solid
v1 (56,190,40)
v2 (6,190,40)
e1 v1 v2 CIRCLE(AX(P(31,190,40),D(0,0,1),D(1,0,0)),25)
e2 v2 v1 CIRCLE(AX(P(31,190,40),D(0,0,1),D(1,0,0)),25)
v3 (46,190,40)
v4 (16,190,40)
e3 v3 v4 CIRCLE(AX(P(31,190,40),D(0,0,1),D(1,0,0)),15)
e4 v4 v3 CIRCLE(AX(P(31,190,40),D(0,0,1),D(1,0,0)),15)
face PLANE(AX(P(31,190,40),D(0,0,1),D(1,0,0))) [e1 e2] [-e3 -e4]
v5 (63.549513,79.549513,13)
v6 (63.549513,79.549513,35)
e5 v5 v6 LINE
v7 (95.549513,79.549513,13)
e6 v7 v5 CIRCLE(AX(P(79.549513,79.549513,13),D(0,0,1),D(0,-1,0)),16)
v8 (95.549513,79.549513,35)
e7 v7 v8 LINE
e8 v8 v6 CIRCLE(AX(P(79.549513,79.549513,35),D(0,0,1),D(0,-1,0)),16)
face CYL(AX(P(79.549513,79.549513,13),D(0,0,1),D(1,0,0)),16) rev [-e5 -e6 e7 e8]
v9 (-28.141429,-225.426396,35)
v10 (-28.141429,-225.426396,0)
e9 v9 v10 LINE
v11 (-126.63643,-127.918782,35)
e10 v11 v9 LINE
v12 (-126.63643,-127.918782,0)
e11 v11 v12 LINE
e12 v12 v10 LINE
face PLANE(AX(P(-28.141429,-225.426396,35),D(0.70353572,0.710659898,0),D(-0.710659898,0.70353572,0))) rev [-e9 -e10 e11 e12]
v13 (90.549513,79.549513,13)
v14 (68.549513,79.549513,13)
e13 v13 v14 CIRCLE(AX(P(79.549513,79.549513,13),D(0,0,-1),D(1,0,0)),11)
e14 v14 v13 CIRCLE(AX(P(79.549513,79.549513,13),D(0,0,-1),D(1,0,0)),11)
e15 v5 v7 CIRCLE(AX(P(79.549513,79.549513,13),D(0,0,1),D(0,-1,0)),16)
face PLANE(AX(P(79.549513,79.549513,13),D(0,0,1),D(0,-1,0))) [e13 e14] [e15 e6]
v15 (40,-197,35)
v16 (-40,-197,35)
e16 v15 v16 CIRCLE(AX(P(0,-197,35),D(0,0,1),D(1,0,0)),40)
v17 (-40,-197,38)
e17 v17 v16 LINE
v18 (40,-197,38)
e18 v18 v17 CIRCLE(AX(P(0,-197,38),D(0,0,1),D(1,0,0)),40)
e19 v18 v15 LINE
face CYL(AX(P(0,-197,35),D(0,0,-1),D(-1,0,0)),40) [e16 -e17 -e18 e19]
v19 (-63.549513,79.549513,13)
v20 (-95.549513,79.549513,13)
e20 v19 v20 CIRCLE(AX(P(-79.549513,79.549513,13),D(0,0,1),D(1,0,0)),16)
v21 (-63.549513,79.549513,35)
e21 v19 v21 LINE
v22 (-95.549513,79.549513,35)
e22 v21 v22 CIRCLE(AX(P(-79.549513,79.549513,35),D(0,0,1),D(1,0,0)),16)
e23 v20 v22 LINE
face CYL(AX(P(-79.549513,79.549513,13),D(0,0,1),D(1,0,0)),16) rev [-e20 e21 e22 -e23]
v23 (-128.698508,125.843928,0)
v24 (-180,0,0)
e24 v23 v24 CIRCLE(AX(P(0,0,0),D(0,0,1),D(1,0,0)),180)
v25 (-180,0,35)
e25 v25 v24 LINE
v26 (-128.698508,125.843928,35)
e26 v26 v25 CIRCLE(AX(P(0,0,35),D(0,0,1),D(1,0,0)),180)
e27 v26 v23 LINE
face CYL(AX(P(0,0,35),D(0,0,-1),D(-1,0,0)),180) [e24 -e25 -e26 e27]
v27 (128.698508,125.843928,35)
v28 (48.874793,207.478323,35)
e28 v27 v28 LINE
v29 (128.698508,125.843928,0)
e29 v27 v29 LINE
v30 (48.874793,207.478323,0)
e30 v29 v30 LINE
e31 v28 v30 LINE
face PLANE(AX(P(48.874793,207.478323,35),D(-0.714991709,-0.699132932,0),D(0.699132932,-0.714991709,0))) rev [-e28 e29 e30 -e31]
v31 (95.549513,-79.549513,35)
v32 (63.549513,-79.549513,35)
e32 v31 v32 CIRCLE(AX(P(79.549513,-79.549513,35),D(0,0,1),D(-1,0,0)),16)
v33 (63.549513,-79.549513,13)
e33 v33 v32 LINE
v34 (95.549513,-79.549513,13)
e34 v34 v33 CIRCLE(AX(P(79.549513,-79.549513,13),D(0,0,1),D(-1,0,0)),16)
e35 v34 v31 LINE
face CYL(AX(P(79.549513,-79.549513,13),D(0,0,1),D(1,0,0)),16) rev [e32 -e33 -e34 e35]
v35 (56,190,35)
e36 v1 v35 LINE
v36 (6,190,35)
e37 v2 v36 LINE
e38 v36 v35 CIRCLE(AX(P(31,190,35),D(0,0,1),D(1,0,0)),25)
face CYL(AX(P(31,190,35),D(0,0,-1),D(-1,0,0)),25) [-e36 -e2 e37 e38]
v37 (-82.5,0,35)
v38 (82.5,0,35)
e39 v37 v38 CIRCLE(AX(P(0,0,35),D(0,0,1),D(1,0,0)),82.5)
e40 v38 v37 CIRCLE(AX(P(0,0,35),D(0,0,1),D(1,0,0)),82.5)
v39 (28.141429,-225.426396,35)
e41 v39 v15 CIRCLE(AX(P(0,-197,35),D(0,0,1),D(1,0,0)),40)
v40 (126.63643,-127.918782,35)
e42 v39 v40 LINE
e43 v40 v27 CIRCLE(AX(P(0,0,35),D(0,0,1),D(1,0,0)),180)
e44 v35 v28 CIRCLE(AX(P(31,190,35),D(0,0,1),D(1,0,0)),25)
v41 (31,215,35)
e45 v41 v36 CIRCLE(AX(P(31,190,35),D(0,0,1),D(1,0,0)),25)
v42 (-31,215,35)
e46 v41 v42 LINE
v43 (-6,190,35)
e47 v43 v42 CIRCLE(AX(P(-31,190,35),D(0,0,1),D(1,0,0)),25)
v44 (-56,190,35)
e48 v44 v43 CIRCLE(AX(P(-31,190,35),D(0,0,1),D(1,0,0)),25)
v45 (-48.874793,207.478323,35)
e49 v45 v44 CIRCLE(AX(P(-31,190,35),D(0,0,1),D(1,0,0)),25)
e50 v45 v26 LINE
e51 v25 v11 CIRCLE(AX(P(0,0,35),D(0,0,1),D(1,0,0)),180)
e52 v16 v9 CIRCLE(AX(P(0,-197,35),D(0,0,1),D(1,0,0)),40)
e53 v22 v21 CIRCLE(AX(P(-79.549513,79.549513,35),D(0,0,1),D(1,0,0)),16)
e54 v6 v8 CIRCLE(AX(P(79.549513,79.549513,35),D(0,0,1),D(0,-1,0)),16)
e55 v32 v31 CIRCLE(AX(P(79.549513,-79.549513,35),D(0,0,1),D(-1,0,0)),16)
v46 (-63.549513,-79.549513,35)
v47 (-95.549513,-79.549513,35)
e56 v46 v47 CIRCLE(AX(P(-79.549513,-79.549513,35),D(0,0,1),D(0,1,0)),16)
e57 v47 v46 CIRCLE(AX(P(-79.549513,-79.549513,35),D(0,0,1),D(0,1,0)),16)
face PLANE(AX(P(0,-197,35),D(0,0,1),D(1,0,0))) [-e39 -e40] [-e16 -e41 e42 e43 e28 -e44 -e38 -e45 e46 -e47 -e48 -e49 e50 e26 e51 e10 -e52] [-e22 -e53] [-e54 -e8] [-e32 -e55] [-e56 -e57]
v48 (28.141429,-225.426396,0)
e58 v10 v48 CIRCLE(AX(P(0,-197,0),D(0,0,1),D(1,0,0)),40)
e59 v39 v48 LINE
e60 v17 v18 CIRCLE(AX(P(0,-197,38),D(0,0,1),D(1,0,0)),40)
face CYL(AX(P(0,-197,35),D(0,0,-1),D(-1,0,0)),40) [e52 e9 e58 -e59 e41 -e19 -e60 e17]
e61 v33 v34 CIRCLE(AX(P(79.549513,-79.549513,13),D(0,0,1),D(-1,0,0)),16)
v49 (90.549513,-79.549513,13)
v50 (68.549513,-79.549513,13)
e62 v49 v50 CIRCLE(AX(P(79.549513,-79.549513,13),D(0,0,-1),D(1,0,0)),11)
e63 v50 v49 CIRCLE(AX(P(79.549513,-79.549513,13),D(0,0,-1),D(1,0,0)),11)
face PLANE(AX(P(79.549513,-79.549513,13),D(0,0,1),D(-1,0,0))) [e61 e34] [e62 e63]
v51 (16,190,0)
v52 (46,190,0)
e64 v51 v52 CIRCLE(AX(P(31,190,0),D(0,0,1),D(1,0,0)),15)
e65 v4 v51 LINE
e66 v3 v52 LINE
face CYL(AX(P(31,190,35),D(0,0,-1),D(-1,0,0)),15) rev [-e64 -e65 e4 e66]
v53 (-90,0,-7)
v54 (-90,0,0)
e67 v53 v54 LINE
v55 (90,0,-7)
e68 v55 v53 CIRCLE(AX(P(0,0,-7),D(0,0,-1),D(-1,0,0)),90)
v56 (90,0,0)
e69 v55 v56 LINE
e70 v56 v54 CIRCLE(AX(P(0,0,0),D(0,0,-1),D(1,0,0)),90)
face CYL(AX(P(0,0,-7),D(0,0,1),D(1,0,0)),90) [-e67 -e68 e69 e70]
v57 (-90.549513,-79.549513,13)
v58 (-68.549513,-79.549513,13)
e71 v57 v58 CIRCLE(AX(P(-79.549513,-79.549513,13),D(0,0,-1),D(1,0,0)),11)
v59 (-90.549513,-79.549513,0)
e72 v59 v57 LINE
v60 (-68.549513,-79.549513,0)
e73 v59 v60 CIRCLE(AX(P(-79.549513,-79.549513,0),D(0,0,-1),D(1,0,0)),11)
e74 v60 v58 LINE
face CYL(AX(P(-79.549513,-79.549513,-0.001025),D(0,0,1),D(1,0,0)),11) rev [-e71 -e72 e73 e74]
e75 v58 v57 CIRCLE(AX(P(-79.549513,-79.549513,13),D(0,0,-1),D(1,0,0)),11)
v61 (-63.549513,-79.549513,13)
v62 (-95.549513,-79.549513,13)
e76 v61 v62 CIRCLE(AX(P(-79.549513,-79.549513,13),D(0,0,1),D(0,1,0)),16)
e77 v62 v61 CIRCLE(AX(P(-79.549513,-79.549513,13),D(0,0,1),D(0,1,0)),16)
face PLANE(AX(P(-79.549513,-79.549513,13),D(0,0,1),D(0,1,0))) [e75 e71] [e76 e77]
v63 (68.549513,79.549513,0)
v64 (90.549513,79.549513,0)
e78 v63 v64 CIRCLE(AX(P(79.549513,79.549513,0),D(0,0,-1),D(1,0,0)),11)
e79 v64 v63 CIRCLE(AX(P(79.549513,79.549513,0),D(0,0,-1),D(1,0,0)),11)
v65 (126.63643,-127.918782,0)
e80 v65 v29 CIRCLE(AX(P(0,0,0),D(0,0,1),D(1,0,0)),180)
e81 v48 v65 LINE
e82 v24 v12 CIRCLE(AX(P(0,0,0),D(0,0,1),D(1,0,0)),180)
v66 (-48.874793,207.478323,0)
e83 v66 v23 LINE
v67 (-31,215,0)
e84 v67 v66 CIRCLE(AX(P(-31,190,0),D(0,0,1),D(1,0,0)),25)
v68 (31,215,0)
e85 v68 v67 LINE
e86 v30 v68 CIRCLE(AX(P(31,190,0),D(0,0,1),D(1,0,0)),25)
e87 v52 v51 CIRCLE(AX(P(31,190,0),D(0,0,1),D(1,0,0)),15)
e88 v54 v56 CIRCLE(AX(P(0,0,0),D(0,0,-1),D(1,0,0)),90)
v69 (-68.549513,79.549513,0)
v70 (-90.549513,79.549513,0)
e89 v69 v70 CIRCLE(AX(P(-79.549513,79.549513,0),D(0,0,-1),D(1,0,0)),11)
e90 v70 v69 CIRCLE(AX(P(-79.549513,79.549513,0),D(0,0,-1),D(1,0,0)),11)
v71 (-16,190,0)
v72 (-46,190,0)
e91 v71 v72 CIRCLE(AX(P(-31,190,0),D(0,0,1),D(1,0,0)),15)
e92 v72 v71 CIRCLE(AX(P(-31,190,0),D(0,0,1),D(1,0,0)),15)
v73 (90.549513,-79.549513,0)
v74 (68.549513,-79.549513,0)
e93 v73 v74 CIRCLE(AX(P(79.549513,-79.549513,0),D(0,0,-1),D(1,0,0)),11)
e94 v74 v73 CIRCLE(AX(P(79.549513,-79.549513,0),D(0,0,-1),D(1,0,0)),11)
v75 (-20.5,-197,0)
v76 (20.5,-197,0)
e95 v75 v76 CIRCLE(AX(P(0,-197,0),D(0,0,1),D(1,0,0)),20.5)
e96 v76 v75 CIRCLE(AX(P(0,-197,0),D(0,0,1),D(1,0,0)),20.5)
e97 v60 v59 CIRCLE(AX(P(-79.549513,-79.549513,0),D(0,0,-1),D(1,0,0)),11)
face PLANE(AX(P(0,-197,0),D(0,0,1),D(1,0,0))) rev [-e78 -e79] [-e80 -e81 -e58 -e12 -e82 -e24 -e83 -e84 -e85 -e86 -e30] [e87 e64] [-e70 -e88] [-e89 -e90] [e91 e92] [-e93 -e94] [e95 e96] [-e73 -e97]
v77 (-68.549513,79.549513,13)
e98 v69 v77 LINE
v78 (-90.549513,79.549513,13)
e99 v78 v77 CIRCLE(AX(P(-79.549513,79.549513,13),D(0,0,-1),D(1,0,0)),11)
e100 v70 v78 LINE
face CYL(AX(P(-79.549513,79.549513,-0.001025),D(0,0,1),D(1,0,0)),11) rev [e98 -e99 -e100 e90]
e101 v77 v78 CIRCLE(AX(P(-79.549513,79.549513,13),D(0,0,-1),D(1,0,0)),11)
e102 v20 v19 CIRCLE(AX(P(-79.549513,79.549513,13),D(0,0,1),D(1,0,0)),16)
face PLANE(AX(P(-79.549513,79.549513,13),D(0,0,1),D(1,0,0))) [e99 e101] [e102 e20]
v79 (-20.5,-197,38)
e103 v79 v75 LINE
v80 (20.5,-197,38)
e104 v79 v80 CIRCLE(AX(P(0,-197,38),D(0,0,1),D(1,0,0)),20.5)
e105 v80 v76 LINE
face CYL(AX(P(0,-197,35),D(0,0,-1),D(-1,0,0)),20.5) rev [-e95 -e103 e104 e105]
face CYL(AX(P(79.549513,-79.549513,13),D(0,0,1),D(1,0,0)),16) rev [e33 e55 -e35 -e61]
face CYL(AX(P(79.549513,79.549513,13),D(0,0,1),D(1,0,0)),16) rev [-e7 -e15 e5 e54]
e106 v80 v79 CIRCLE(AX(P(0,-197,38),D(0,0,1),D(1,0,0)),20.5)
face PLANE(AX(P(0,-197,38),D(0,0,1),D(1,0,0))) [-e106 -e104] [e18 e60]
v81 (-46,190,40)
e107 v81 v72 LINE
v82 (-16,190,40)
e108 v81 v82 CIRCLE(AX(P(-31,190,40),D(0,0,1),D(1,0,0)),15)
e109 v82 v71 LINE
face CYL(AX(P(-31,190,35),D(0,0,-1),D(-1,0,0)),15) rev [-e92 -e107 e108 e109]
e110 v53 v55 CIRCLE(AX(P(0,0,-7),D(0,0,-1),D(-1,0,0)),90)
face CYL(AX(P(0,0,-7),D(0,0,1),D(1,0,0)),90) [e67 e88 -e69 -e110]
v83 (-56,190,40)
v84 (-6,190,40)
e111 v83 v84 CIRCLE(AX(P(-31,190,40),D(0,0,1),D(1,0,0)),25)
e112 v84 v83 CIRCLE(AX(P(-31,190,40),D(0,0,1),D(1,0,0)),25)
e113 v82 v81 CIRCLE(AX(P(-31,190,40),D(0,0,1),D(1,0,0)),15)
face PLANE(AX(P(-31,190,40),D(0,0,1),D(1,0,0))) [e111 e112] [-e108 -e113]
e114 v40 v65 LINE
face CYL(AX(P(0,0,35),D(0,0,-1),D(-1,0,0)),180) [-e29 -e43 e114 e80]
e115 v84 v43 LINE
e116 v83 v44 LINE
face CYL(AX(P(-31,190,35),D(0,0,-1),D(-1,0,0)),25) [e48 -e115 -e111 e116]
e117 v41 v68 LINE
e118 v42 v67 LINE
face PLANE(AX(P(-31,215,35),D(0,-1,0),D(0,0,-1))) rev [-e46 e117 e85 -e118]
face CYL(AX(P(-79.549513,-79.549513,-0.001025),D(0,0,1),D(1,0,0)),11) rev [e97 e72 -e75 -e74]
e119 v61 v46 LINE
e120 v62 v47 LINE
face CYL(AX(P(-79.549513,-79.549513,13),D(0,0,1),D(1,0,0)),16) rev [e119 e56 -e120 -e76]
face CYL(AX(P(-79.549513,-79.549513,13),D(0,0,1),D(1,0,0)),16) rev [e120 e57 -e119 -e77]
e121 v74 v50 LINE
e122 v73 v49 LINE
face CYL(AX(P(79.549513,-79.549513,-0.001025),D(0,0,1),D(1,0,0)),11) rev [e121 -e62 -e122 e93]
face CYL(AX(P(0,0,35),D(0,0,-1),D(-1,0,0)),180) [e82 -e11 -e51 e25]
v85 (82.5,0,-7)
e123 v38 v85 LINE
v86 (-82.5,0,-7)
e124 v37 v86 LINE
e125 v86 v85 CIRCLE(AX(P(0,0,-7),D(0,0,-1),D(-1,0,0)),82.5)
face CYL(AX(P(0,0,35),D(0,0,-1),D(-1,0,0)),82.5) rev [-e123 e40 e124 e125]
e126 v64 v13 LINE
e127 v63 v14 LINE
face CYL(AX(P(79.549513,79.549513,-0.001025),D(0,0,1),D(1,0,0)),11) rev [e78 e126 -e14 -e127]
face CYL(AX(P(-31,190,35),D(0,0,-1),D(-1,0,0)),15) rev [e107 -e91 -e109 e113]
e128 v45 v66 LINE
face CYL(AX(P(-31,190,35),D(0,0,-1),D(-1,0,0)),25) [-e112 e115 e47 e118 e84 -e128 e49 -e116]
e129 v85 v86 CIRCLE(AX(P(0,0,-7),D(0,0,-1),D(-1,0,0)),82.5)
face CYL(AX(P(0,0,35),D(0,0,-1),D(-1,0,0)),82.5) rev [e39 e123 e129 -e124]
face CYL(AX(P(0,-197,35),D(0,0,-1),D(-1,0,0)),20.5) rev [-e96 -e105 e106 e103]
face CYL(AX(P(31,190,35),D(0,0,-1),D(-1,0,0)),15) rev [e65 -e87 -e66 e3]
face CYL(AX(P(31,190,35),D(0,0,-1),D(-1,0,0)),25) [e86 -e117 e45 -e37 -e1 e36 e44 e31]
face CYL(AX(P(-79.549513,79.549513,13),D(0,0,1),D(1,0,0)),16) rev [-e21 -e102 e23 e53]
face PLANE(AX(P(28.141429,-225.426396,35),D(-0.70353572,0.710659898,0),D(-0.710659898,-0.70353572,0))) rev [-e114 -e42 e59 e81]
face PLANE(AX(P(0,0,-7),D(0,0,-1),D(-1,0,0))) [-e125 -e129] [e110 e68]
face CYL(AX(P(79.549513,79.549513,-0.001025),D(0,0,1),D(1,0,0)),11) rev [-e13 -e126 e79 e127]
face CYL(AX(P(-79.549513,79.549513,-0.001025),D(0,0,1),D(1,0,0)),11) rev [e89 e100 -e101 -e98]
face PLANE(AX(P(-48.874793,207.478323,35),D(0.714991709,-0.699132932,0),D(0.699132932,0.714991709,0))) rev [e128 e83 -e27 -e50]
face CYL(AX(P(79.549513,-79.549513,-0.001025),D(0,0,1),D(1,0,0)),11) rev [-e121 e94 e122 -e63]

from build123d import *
from build123d.topology import SkipClean

# Parameters (mm, degrees)
SKETCH1_R          = 15
SKETCH1_R_2        = 20.5
SKETCH1_R_3        = 82.5
EXTRUDE1_DEPTH     = 35
SKETCH2_R          = 25
SKETCH2_R_2        = 15
EXTRUDE2_DEPTH     = 5
CUT_EXTRUDE1_REACH = 301.656
SKETCH3_R          = 11
SKETCH5_R          = 16
CUT_EXTRUDE9_DEPTH = 22
CIRPATTERN1_COUNT  = 4
SKETCH8_R          = 40
SKETCH8_R_2        = 20.5
EXTRUDE5_DEPTH     = 3
EXTRUDE6_START     = 7
SKETCH9_R          = 90
SKETCH9_R_2        = 82.5
EXTRUDE6_DEPTH     = 7


with BuildPart() as part:
    # Sketch1 → Extrude1 (new body)
    with BuildSketch(Plane.XY):
        with BuildLine():
            Line((-48.874792723, 207.478323293), (-128.698507603, 125.843927707))
            ThreePointArc((-128.698507603, 125.843927707), (-179.994057412, -1.462633346), (-126.636429521, -127.918781726))
            Line((-126.636429521, -127.918781726), (-28.141428782, -225.426395939))
            ThreePointArc((-28.141428782, -225.426395939), (0, -237), (28.141428782, -225.426395939))
            Line((28.141428782, -225.426395939), (126.636429521, -127.918781726))
            ThreePointArc((126.636429521, -127.918781726), (179.994057412, -1.462633346), (128.698507603, 125.843927707))
            Line((128.698507603, 125.843927707), (48.874792723, 207.478323293))
            ThreePointArc((48.874792723, 207.478323293), (40.696440524, 213.042982471), (31, 215))
            Line((31, 215), (-31, 215))
            ThreePointArc((-31, 215), (-40.696440524, 213.042982471), (-48.874792723, 207.478323293))
        make_face()
        with Locations((-31, 190)):
            Circle(SKETCH1_R, mode=Mode.SUBTRACT)
        with Locations((31, 190)):
            Circle(SKETCH1_R, mode=Mode.SUBTRACT)
        with Locations((0, -197)):
            Circle(SKETCH1_R_2, mode=Mode.SUBTRACT)
        Circle(SKETCH1_R_3, mode=Mode.SUBTRACT)
    extrude(amount=EXTRUDE1_DEPTH)

    # Sketch2 → Extrude2 (add)
    # profile 1 of 2: a face of its own
    with BuildSketch(Plane.XY.offset(35)):
        with Locations(Location((-31, 190, 0), (0, 0, 135.642519681))):
            Circle(SKETCH2_R)
        with Locations((-31, 190)):
            Circle(SKETCH2_R_2, mode=Mode.SUBTRACT)
    # profile 2 of 2: a face of its own
    with BuildSketch(Plane.XY.offset(35)):
        with Locations(Location((31, 190, 0), (0, 0, 90))):
            Circle(SKETCH2_R)
        with Locations((31, 190)):
            Circle(SKETCH2_R_2, mode=Mode.SUBTRACT)
    extrude(amount=EXTRUDE2_DEPTH)

    # Sketch3 → Cut-Extrude1 (cut, up to next)
    with BuildSketch(Plane.XY.offset(35), mode=Mode.PRIVATE) as cut_extrude1_sk1:
        with Locations((-79.549512883, 79.549512883)):
            Circle(SKETCH3_R)
    cut_extrude1_tool1 = extrude(cut_extrude1_sk1.sketch, amount=-CUT_EXTRUDE1_REACH, mode=Mode.PRIVATE) & part.part
    # Sketch3 → Cut-Extrude1 (cut, up to next)
    with BuildSketch(Plane.XY.offset(35), mode=Mode.PRIVATE) as cut_extrude1_sk2:
        with Locations((-79.549512883, -79.549512883)):
            Circle(SKETCH3_R)
    cut_extrude1_tool2 = extrude(cut_extrude1_sk2.sketch, amount=-CUT_EXTRUDE1_REACH, mode=Mode.PRIVATE) & part.part
    # Sketch3 → Cut-Extrude1 (cut, up to next)
    with BuildSketch(Plane.XY.offset(35), mode=Mode.PRIVATE) as cut_extrude1_sk3:
        with Locations((79.549512883, -79.549512883)):
            Circle(SKETCH3_R)
    cut_extrude1_tool3 = extrude(cut_extrude1_sk3.sketch, amount=-CUT_EXTRUDE1_REACH, mode=Mode.PRIVATE) & part.part
    # Sketch3 → Cut-Extrude1 (cut, up to next)
    with BuildSketch(Plane.XY.offset(35), mode=Mode.PRIVATE) as cut_extrude1_sk4:
        with Locations((79.549512883, 79.549512883)):
            Circle(SKETCH3_R)
    cut_extrude1_tool4 = extrude(cut_extrude1_sk4.sketch, amount=-CUT_EXTRUDE1_REACH, mode=Mode.PRIVATE) & part.part
    add(cut_extrude1_tool1.solids().sort_by_distance((-79.549513, 79.549513, 35))[0], mode=Mode.SUBTRACT)
    add(cut_extrude1_tool2.solids().sort_by_distance((-79.549513, -79.549513, 35))[0], mode=Mode.SUBTRACT)
    add(cut_extrude1_tool3.solids().sort_by_distance((79.549513, -79.549513, 35))[0], mode=Mode.SUBTRACT)
    add(cut_extrude1_tool4.solids().sort_by_distance((79.549513, 79.549513, 35))[0], mode=Mode.SUBTRACT)

    # Sketch5 → Cut-Extrude9 (cut)
    with BuildSketch(Plane.XY.offset(35)):
        with Locations((-79.549512883, 79.549512883)):
            Circle(SKETCH5_R)
    cut_extrude9 = extrude(amount=-CUT_EXTRUDE9_DEPTH, mode=Mode.SUBTRACT)

    # CirPattern1: Cut-Extrude9 ×4 about axis
    cirpattern1_axis = Axis((0, 0, 0), (0, 0, 1))
    for i in range(1, CIRPATTERN1_COUNT):
        add(cut_extrude9.rotate(cirpattern1_axis, i * 360 / CIRPATTERN1_COUNT), mode=Mode.SUBTRACT)

    # Sketch8 → Extrude5 (add)
    with BuildSketch(Plane.XY.offset(35)):
        with Locations(Location((0, -197, 0), (0, 0, 225.288631874))):
            Circle(SKETCH8_R)
        with Locations((0, -197)):
            Circle(SKETCH8_R_2, mode=Mode.SUBTRACT)
    extrude(amount=EXTRUDE5_DEPTH)

    # Sketch9 → Extrude6 (add)
    with SkipClean():  # the faces are left unmerged after this step: merging them gives an invalid solid
        with BuildSketch(Plane(origin=(0, 0, 0), x_dir=(-1, 0, 0), z_dir=(0, 0, -1)).offset(EXTRUDE6_START)):
            with Locations(Location((0, 0, 0), (0, 0, 180))):
                Circle(SKETCH9_R)
            Circle(SKETCH9_R_2, mode=Mode.SUBTRACT)
        extrude(amount=-EXTRUDE6_DEPTH)


solid = part.part
